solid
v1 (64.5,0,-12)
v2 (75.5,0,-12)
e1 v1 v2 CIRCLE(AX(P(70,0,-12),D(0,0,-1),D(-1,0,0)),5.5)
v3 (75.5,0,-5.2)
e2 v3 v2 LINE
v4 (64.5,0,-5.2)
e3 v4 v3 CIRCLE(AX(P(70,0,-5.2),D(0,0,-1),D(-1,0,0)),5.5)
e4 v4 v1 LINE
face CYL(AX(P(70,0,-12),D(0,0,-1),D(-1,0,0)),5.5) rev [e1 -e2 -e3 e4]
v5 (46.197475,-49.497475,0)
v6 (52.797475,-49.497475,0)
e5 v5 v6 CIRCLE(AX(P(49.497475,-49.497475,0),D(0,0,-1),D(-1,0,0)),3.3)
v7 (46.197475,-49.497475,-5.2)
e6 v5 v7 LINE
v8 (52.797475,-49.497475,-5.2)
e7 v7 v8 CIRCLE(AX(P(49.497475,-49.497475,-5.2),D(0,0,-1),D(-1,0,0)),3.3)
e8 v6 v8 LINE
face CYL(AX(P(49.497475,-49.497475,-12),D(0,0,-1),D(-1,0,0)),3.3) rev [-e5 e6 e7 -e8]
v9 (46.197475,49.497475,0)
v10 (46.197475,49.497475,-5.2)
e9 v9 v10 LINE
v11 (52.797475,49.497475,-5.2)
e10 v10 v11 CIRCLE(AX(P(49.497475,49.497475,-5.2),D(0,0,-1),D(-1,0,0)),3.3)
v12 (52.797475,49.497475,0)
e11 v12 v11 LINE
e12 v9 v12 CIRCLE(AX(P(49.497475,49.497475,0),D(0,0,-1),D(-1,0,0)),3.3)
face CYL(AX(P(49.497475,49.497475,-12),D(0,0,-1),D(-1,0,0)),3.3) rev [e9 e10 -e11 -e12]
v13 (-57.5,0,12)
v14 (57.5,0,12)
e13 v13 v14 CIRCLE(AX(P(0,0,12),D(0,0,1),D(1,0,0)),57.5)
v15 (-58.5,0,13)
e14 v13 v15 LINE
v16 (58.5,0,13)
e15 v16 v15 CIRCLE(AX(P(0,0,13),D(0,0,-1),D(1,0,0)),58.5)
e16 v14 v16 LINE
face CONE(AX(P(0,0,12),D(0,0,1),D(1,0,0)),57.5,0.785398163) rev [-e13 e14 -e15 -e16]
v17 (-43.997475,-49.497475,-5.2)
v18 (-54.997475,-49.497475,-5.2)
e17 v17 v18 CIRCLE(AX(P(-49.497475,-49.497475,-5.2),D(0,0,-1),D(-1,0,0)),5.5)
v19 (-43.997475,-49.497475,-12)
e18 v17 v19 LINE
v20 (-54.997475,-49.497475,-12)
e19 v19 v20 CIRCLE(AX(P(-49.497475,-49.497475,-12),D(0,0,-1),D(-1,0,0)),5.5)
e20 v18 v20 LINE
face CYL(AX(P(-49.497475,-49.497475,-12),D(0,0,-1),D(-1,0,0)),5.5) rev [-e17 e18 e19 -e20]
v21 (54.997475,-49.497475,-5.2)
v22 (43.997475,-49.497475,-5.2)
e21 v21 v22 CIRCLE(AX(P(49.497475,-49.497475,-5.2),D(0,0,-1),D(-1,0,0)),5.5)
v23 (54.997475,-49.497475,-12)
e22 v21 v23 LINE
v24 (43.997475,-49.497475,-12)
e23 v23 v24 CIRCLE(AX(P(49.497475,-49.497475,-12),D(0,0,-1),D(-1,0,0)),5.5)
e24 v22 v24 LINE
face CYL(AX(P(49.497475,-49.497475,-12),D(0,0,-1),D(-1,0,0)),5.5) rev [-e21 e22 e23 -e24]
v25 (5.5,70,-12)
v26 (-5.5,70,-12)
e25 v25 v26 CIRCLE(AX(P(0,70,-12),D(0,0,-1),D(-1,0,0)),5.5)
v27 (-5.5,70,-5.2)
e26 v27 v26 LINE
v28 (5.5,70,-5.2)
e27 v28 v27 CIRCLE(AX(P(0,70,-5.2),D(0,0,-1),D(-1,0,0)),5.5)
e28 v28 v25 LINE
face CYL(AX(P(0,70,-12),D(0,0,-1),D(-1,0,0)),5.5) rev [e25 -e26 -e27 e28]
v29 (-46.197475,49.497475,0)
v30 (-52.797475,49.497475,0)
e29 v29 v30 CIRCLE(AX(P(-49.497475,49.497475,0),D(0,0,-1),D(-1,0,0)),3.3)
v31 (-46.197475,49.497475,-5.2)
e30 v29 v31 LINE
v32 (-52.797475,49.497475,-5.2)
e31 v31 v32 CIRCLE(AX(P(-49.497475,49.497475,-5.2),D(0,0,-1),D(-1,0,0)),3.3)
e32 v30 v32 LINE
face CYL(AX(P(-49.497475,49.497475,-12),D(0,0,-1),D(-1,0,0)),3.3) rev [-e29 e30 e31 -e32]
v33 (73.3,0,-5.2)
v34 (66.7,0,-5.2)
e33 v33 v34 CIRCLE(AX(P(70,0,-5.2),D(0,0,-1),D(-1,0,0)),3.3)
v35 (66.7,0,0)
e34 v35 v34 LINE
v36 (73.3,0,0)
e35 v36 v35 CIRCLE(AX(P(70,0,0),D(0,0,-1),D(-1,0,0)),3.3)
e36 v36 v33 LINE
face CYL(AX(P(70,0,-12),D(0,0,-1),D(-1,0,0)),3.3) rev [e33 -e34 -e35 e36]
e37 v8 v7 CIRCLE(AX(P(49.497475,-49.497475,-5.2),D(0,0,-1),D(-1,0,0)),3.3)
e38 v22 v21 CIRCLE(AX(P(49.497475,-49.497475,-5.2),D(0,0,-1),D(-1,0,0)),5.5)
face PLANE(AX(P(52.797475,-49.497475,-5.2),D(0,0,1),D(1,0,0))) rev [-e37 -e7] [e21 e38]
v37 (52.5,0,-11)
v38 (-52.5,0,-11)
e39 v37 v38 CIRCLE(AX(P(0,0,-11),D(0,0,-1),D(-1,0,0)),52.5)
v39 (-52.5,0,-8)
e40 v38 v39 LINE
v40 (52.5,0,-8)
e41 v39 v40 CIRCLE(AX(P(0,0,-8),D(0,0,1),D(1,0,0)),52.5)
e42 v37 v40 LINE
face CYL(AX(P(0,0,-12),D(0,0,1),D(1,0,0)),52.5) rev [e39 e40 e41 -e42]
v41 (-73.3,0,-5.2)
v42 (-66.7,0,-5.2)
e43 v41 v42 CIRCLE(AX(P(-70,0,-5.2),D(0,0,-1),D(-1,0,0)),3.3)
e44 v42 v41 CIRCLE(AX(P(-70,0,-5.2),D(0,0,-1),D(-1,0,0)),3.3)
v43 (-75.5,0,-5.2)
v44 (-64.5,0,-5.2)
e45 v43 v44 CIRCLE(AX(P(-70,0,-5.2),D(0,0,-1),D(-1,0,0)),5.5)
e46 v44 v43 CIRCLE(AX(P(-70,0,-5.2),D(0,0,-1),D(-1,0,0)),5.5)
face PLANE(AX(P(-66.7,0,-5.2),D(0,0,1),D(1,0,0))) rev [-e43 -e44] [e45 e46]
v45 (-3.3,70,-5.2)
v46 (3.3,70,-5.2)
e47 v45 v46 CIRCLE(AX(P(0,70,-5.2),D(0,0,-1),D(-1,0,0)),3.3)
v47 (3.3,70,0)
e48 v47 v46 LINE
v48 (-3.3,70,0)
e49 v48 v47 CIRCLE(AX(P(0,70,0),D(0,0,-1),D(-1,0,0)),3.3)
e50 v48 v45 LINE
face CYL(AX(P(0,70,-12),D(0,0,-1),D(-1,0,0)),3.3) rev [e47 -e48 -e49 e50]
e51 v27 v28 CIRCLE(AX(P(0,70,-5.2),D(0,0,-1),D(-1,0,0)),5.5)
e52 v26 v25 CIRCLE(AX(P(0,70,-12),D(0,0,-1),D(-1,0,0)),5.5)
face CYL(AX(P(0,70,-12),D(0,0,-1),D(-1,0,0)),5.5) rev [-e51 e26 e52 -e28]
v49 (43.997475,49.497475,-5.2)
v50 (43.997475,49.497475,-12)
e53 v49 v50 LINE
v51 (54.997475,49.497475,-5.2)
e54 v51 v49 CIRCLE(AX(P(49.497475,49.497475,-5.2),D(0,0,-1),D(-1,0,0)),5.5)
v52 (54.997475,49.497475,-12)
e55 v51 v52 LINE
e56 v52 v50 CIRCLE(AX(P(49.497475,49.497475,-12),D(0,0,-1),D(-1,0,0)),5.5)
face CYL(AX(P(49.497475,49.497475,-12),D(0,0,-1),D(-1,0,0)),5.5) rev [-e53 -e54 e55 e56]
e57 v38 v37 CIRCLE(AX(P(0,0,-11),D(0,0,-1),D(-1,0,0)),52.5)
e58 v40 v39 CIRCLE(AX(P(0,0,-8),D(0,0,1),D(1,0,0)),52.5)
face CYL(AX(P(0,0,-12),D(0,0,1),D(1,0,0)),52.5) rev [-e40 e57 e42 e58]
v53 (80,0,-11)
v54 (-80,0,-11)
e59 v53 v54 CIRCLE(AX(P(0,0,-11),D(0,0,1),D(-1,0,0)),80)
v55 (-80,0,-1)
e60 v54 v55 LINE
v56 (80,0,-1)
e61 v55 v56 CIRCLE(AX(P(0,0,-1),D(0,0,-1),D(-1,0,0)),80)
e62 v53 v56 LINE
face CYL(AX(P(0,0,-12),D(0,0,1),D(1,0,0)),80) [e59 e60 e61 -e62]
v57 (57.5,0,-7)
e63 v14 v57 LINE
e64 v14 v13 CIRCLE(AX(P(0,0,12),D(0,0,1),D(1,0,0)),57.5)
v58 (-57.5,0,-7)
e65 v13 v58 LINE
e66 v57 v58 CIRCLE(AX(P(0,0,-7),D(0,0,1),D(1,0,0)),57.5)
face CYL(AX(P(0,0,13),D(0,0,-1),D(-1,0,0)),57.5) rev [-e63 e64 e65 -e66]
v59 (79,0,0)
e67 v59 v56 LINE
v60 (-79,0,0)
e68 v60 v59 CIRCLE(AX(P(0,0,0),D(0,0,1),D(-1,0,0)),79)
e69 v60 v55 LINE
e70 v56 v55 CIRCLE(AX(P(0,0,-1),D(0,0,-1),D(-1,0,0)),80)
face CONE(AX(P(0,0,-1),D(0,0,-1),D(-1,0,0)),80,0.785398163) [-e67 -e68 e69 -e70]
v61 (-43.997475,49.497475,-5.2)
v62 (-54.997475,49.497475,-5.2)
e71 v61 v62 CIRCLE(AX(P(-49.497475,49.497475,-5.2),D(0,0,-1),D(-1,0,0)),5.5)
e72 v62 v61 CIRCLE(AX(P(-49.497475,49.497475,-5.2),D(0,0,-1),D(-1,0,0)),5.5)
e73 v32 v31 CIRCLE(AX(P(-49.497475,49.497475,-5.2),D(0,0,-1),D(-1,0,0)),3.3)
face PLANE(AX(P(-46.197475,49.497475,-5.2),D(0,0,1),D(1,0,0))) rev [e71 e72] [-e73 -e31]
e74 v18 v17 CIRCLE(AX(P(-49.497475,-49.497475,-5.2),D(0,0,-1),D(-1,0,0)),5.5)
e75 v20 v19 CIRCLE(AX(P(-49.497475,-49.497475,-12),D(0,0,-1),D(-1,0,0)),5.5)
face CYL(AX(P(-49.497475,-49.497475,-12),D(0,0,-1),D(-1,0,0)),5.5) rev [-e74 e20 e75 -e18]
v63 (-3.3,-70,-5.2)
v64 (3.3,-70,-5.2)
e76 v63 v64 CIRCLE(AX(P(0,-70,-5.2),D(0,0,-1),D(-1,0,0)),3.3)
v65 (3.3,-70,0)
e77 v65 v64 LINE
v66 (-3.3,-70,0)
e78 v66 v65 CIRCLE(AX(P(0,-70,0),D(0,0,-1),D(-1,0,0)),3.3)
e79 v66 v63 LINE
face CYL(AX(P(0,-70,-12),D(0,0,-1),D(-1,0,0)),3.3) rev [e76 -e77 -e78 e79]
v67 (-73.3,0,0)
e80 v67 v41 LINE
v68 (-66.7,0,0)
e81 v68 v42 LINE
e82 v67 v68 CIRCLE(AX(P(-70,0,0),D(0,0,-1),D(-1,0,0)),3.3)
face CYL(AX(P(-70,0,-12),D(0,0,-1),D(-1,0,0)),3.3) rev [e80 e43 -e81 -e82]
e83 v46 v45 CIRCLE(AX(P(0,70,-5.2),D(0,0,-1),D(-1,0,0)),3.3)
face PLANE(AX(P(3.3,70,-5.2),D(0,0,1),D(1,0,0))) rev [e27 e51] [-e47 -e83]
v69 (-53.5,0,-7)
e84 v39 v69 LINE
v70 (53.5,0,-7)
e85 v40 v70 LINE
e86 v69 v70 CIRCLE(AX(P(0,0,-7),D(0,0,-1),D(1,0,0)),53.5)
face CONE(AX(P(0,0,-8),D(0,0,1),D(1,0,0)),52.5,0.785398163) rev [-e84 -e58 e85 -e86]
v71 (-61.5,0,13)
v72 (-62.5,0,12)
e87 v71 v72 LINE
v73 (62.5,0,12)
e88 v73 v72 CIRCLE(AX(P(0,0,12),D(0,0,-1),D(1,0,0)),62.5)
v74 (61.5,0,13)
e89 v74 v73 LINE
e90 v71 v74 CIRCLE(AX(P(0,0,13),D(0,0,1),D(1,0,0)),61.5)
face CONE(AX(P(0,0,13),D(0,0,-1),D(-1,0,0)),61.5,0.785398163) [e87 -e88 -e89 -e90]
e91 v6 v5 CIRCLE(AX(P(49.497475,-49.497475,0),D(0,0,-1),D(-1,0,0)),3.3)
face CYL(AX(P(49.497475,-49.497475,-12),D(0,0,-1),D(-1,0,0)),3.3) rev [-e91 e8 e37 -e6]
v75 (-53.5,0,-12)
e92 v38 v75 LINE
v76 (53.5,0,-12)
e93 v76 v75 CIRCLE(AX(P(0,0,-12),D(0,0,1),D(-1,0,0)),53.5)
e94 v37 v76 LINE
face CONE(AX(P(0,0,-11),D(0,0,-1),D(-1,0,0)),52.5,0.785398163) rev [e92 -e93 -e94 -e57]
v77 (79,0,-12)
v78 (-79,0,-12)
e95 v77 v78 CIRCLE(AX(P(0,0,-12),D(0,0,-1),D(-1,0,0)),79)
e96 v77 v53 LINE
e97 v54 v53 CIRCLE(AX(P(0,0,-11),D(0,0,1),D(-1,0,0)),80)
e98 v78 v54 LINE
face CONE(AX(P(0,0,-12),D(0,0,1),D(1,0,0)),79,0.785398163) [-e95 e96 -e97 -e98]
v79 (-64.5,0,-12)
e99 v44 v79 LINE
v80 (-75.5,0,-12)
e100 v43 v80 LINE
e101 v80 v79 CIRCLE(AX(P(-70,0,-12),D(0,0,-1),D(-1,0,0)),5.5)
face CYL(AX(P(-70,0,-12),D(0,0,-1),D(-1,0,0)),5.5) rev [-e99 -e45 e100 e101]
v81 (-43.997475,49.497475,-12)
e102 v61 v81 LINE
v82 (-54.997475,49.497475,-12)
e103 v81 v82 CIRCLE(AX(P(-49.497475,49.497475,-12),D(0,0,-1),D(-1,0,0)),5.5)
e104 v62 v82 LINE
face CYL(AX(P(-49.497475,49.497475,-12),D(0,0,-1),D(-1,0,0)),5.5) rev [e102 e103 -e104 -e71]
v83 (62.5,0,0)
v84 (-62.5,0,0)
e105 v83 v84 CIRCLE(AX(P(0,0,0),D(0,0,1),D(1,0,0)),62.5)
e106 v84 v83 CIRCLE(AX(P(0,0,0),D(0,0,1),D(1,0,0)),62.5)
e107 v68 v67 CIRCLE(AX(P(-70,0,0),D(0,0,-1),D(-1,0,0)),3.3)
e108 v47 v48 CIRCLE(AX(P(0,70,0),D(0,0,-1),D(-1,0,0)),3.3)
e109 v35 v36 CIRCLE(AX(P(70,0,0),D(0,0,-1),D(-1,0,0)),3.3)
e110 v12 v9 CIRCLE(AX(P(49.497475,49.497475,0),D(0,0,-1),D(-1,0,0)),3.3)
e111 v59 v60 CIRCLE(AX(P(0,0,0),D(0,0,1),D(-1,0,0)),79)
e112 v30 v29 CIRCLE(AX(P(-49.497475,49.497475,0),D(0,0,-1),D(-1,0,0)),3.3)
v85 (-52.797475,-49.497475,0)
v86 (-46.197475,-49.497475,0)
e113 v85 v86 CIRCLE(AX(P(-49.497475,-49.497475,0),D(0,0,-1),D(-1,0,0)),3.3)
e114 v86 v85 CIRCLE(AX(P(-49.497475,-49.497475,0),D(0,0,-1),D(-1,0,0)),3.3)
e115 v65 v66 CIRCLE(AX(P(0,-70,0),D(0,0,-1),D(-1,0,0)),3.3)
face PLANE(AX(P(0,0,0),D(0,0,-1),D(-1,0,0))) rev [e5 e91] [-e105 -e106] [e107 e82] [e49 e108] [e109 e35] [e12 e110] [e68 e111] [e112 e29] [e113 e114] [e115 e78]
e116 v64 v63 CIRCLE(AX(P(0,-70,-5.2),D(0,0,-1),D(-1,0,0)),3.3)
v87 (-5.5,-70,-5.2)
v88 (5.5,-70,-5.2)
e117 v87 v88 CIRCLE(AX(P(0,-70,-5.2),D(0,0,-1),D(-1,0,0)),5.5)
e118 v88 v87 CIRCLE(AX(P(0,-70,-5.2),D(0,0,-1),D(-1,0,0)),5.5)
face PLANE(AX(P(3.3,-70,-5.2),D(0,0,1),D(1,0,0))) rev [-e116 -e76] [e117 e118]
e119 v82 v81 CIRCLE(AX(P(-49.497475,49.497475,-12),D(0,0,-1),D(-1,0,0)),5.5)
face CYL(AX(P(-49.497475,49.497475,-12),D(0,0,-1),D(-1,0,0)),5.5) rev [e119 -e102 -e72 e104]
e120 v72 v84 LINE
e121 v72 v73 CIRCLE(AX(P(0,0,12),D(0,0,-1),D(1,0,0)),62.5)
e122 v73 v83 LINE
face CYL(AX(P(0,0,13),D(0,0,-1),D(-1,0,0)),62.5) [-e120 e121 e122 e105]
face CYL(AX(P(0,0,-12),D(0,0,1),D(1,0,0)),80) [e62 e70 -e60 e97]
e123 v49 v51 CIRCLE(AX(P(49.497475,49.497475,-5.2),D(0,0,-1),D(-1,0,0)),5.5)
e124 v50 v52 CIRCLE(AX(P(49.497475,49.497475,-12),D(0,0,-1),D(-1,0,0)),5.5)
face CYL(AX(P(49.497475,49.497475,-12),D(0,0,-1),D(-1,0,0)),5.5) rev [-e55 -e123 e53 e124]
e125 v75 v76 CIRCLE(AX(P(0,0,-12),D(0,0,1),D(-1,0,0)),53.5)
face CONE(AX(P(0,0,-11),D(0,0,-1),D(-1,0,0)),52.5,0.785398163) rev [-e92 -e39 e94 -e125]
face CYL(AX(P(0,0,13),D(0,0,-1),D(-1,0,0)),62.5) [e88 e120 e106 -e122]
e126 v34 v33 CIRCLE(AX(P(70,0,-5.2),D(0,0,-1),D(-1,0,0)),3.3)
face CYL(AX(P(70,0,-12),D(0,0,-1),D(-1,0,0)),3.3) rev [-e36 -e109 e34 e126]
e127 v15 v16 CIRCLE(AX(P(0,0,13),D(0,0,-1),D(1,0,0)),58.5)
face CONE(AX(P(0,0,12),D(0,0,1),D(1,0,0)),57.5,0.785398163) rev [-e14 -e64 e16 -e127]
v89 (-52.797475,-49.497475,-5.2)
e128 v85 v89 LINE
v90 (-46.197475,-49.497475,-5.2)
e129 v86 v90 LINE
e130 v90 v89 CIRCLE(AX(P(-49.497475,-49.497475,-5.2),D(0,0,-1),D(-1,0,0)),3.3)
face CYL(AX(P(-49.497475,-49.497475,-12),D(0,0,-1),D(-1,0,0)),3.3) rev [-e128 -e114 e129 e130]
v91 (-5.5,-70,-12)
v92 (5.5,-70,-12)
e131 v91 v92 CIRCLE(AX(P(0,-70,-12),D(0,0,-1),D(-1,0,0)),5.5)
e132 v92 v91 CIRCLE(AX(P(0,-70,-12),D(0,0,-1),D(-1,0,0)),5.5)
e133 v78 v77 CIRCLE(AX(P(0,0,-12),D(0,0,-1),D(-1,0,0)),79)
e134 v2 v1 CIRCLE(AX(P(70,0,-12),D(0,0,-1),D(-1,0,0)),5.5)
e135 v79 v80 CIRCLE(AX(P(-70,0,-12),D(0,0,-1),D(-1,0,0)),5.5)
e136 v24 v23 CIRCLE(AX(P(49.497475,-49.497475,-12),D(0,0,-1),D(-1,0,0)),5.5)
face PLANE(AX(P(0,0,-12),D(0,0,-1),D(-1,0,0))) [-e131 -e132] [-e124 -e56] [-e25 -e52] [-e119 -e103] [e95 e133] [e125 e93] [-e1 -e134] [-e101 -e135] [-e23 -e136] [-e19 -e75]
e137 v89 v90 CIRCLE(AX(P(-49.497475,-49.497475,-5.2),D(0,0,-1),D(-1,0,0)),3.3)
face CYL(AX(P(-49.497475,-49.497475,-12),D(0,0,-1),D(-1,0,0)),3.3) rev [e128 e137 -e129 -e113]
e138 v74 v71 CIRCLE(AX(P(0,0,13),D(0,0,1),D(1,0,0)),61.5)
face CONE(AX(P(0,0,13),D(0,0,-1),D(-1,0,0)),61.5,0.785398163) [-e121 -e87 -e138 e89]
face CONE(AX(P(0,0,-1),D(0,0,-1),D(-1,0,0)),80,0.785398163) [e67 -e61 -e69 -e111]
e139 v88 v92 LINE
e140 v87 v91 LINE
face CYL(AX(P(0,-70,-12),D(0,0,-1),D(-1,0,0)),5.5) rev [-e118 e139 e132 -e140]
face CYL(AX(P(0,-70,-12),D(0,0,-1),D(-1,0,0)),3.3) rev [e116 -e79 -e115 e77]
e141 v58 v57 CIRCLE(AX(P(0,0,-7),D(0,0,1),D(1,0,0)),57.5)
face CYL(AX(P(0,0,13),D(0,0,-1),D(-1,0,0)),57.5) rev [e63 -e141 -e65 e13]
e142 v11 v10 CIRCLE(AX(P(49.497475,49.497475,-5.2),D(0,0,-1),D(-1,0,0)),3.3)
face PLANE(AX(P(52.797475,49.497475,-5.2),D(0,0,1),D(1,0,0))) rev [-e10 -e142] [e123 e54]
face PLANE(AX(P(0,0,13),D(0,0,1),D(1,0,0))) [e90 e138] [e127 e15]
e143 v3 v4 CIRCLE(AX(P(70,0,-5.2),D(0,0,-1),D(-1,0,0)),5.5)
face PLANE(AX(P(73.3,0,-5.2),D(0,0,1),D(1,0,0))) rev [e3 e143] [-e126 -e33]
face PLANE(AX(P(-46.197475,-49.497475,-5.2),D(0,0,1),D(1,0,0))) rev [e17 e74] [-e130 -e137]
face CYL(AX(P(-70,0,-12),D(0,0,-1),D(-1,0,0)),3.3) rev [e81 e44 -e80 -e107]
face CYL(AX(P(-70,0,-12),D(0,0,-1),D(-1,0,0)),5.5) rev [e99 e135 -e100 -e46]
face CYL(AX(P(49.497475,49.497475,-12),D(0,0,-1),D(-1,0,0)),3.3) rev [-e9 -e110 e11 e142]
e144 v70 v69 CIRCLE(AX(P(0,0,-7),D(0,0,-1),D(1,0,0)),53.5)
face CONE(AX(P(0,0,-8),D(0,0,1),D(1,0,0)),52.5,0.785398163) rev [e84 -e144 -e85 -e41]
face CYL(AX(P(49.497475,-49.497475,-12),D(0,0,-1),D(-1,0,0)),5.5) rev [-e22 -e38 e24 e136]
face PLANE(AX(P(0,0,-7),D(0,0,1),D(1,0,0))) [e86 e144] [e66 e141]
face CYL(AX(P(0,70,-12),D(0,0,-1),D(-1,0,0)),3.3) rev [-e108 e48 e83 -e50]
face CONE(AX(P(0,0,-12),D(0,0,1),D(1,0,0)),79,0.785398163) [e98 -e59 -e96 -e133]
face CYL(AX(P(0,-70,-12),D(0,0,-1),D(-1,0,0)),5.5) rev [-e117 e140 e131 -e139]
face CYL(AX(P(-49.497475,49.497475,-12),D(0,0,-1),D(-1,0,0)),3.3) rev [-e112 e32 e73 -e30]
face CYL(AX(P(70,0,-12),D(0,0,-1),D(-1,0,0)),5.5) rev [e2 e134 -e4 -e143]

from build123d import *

# Parameters (mm, degrees)
SKETCH1_R           = 62.5
SKETCH1_R_2         = 57.5
BOSS_EXTRUDE1_DEPTH = 13
SKETCH2_R           = 80
SKETCH2_R_2         = 52.5
BOSS_EXTRUDE2_DEPTH = 12
CUT_EXTRUDE1_START  = -7
SKETCH3_R           = 57.5
CUT_EXTRUDE1_DEPTH  = 7
CIRPATTERN1_COUNT   = 8
CHAMFER1_SIZE       = 1


with BuildPart() as part:
    # Sketch1 → Boss-Extrude1 (new body)
    with BuildSketch(Plane.XY):
        Circle(SKETCH1_R)
        Circle(SKETCH1_R_2, mode=Mode.SUBTRACT)
    extrude(amount=BOSS_EXTRUDE1_DEPTH)

    # Sketch2 → Boss-Extrude2 (add)
    with BuildSketch(Plane(origin=(0, 0, 0), x_dir=(-1, 0, 0), z_dir=(0, 0, -1))):
        Circle(SKETCH2_R)
        Circle(SKETCH2_R_2, mode=Mode.SUBTRACT)
    extrude(amount=BOSS_EXTRUDE2_DEPTH)

    # Sketch3 → Cut-Extrude1 (cut)
    with BuildSketch(Plane.XY.offset(CUT_EXTRUDE1_START)):
        Circle(SKETCH3_R)
    extrude(amount=CUT_EXTRUDE1_DEPTH, mode=Mode.SUBTRACT)

    # Sketch5 → Hole size (%based on) socket head cap screw type1 (revolve, cut)
    with BuildSketch(Plane(origin=(-70, 0, -12), x_dir=(0, 1, 0), z_dir=(1, 0, 0))):
        Polygon((0, 0), (0, 26.482840043), (3.3, 24.5), (3.3, 6.8), (5.5, 6.8), (5.5, 0), align=None)
    hole_size_based_on_socket_head_cap_scr = revolve(axis=Axis((-70, 0, -18.35), (0, 0, 1)), mode=Mode.SUBTRACT)

    # CirPattern1: Hole size (%based on) socket head cap screw type1 ×8 about axis
    cirpattern1_axis = Axis((0, 0, 0), (0, 0, 1))
    for i in range(1, CIRPATTERN1_COUNT):
        add(hole_size_based_on_socket_head_cap_scr.rotate(cirpattern1_axis, i * 360 / CIRPATTERN1_COUNT), mode=Mode.SUBTRACT)

    # Chamfer1
    chamfer1_edges = [part.edges().sort_by_distance(p)[0] for p in [
        (80, 0, -12),
        (80, 0, 0),
        (52.5, 0, -12),
        (52.5, 0, -7),
        (-62.5, 0, 13),
        (-57.5, 0, 13),
    ]]
    chamfer(chamfer1_edges, length=CHAMFER1_SIZE)


solid = part.part
